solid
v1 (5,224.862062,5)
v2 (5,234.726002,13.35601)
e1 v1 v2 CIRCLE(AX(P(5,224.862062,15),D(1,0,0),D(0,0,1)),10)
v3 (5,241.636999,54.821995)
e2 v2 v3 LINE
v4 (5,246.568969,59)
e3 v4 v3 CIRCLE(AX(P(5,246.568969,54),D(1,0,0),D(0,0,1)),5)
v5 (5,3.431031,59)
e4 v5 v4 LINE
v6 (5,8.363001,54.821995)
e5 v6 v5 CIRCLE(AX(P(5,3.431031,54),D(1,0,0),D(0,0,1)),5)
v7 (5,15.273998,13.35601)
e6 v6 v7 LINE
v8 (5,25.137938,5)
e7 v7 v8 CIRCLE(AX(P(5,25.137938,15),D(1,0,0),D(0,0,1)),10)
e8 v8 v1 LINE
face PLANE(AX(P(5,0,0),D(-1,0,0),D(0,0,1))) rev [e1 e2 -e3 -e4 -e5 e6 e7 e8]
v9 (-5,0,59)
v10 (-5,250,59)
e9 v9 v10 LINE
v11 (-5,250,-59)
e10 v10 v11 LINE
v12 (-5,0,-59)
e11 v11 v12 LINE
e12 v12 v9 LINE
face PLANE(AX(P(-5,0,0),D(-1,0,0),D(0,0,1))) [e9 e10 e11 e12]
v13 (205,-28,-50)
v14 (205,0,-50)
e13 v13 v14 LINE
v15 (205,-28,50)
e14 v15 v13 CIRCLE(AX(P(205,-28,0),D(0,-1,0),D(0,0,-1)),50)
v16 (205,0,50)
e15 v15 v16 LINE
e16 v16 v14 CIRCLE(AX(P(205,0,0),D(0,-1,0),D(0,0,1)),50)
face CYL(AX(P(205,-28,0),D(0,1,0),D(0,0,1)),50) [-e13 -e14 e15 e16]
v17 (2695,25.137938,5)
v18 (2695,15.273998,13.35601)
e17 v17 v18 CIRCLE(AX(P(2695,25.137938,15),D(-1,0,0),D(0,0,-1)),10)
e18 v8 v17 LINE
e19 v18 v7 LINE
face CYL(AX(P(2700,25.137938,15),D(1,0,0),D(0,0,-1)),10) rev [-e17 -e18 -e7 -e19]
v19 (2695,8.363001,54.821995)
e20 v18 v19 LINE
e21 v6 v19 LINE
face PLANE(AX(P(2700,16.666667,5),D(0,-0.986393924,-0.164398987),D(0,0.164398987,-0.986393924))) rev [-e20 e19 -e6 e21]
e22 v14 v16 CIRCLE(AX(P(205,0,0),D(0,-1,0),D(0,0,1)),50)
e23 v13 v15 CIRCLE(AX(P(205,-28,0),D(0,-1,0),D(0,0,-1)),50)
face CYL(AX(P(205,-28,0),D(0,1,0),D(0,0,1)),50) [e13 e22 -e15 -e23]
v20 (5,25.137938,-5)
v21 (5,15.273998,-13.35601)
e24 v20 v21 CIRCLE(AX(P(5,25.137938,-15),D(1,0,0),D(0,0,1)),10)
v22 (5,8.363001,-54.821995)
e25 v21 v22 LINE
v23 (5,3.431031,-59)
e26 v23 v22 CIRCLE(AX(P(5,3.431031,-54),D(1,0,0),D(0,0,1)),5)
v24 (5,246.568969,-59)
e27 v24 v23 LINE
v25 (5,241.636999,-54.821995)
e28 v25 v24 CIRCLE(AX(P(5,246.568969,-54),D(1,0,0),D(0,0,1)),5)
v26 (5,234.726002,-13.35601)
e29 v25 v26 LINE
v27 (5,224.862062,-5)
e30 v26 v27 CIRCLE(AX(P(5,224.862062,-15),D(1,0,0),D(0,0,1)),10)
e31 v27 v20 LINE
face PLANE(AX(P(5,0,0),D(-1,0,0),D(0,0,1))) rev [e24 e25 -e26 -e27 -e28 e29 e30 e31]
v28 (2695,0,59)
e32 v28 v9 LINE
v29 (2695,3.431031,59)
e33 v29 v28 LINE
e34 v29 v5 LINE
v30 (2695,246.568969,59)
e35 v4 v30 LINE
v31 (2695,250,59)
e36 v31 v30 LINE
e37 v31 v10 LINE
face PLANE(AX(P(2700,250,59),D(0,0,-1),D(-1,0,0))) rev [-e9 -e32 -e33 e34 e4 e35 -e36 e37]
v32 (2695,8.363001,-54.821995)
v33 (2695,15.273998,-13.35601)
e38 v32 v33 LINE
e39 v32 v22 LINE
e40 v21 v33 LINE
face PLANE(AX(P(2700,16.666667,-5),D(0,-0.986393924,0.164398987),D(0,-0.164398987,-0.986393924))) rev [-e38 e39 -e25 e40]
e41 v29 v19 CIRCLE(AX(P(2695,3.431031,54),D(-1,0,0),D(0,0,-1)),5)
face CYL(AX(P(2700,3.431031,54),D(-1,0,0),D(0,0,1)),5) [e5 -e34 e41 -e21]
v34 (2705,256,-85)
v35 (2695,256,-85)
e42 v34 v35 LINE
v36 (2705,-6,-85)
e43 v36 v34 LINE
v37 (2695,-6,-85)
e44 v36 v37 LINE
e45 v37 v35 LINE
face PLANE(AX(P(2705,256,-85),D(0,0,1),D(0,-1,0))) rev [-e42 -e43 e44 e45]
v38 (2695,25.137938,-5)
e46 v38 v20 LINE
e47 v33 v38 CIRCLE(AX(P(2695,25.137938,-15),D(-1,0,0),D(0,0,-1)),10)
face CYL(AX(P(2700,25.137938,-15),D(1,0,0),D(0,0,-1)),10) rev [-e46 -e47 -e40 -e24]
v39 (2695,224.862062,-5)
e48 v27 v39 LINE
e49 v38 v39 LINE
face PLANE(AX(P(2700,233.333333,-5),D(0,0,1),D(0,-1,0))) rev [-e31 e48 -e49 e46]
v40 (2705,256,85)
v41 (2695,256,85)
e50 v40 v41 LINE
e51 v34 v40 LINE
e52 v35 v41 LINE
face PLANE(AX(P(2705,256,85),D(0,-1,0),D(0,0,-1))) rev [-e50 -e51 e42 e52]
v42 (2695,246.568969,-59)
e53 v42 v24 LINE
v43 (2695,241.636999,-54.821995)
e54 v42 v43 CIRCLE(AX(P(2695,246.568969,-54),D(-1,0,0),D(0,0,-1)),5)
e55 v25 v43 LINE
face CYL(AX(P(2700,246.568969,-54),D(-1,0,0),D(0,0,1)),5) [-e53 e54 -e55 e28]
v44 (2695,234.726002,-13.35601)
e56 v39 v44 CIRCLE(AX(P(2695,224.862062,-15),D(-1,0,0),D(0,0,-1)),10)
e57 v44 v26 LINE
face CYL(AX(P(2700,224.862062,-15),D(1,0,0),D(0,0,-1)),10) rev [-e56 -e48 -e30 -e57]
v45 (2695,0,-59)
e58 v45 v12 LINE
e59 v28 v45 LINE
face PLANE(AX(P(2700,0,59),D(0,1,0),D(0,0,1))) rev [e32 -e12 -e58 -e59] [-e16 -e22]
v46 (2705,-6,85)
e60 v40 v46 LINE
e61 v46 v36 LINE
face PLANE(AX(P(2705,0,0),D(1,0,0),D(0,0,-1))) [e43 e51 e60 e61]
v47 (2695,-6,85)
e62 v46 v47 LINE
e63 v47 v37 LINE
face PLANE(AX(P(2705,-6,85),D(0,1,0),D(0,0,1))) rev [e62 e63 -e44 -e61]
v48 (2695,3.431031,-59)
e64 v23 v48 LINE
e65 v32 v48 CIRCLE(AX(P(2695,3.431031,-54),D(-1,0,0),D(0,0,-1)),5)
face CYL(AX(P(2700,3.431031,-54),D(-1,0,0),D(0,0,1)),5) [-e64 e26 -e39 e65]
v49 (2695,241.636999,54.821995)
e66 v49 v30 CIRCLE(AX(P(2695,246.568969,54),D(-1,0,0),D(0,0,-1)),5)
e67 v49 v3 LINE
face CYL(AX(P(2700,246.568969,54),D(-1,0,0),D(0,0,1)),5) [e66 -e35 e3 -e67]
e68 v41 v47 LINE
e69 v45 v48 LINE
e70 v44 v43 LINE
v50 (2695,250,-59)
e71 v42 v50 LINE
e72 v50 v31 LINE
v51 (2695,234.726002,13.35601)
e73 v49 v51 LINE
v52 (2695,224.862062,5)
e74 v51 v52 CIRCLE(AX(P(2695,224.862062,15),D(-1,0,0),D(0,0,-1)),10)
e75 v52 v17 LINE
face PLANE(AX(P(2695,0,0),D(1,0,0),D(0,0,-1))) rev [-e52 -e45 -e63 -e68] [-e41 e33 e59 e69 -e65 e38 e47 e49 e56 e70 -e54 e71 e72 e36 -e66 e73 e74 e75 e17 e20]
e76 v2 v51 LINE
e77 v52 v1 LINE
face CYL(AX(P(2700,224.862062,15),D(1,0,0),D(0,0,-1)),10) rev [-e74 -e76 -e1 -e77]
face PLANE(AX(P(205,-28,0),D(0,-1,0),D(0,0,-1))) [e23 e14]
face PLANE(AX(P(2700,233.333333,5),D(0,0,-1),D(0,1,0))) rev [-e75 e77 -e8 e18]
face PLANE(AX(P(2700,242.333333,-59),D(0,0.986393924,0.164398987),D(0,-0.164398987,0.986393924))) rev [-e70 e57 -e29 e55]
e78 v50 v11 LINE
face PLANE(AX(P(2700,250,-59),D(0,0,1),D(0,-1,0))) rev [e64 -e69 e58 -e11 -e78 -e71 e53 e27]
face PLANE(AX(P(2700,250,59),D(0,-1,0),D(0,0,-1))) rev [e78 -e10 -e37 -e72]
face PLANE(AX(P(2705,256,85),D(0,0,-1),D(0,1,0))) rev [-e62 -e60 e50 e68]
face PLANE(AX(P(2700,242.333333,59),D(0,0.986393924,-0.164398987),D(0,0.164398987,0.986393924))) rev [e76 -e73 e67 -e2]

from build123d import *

# Parameters (mm, degrees)
BASE_DEPTH          = 2700
FILLET1_R           = 10
FILLET2_R           = 5
SKETCH_1_W          = 118
SKETCH_1_H          = 250
BOSS_EXTRUDE1_DEPTH = 5
SKETCH2_W           = 170
SKETCH2_H           = 262
BOSS_EXTRUDE2_DEPTH = 5
SKETCH3_R           = 50
BOSS_EXTRUDE3_DEPTH = 28


with BuildPart() as part:
    # Sketch1 → Base (new body)
    with BuildSketch(Plane(origin=(0, 0, 0), x_dir=(0, 0, -1), z_dir=(1, 0, 0))):
        Polygon((-59, 0), (59, 0), (59, 7.666666667), (5, 16.666666667), (5, 233.333333333), (59, 242.333333333), (59, 250), (-59, 250), (-59, 242.333333333), (-5, 233.333333333), (-5, 16.666666667), (-59, 7.666666667), align=None)
    extrude(amount=BASE_DEPTH)

    # Fillet1
    fillet1_edges = [part.edges().sort_by_distance(p)[0] for p in [
        (1350, 16.666666667, 5),
        (1350, 233.333333333, 5),
        (1350, 233.333333333, -5),
        (1350, 16.666666667, -5),
    ]]
    fillet(fillet1_edges, radius=FILLET1_R)

    # Fillet2
    fillet2_edges = [part.edges().sort_by_distance(p)[0] for p in [
        (1350, 7.666666667, 59),
        (1350, 242.333333333, 59),
        (1350, 242.333333333, -59),
        (1350, 7.666666667, -59),
    ]]
    fillet(fillet2_edges, radius=FILLET2_R)

    # 草图1 → Boss-Extrude1 (add, symmetric)
    with BuildSketch(Plane.ZY):
        with Locations((0, 125)):
            Rectangle(SKETCH_1_W, SKETCH_1_H)
    extrude(amount=BOSS_EXTRUDE1_DEPTH, both=True)

    # Sketch2 → Boss-Extrude2 (add, symmetric)
    with BuildSketch(Plane(origin=(2700, 0, 0), x_dir=(0, 0, -1), z_dir=(1, 0, 0))):
        with Locations((0, 125)):
            Rectangle(SKETCH2_W, SKETCH2_H)
    extrude(amount=BOSS_EXTRUDE2_DEPTH, both=True)

    # Sketch3 → Boss-Extrude3 (add)
    with BuildSketch(Plane(origin=(0, 0, 0), x_dir=(-1, 0, 0), z_dir=(0, -1, 0))):
        with Locations(Location((-205, 0, 0), (0, 0, 270))):
            Circle(SKETCH3_R)
    extrude(amount=BOSS_EXTRUDE3_DEPTH)


solid = part.part
